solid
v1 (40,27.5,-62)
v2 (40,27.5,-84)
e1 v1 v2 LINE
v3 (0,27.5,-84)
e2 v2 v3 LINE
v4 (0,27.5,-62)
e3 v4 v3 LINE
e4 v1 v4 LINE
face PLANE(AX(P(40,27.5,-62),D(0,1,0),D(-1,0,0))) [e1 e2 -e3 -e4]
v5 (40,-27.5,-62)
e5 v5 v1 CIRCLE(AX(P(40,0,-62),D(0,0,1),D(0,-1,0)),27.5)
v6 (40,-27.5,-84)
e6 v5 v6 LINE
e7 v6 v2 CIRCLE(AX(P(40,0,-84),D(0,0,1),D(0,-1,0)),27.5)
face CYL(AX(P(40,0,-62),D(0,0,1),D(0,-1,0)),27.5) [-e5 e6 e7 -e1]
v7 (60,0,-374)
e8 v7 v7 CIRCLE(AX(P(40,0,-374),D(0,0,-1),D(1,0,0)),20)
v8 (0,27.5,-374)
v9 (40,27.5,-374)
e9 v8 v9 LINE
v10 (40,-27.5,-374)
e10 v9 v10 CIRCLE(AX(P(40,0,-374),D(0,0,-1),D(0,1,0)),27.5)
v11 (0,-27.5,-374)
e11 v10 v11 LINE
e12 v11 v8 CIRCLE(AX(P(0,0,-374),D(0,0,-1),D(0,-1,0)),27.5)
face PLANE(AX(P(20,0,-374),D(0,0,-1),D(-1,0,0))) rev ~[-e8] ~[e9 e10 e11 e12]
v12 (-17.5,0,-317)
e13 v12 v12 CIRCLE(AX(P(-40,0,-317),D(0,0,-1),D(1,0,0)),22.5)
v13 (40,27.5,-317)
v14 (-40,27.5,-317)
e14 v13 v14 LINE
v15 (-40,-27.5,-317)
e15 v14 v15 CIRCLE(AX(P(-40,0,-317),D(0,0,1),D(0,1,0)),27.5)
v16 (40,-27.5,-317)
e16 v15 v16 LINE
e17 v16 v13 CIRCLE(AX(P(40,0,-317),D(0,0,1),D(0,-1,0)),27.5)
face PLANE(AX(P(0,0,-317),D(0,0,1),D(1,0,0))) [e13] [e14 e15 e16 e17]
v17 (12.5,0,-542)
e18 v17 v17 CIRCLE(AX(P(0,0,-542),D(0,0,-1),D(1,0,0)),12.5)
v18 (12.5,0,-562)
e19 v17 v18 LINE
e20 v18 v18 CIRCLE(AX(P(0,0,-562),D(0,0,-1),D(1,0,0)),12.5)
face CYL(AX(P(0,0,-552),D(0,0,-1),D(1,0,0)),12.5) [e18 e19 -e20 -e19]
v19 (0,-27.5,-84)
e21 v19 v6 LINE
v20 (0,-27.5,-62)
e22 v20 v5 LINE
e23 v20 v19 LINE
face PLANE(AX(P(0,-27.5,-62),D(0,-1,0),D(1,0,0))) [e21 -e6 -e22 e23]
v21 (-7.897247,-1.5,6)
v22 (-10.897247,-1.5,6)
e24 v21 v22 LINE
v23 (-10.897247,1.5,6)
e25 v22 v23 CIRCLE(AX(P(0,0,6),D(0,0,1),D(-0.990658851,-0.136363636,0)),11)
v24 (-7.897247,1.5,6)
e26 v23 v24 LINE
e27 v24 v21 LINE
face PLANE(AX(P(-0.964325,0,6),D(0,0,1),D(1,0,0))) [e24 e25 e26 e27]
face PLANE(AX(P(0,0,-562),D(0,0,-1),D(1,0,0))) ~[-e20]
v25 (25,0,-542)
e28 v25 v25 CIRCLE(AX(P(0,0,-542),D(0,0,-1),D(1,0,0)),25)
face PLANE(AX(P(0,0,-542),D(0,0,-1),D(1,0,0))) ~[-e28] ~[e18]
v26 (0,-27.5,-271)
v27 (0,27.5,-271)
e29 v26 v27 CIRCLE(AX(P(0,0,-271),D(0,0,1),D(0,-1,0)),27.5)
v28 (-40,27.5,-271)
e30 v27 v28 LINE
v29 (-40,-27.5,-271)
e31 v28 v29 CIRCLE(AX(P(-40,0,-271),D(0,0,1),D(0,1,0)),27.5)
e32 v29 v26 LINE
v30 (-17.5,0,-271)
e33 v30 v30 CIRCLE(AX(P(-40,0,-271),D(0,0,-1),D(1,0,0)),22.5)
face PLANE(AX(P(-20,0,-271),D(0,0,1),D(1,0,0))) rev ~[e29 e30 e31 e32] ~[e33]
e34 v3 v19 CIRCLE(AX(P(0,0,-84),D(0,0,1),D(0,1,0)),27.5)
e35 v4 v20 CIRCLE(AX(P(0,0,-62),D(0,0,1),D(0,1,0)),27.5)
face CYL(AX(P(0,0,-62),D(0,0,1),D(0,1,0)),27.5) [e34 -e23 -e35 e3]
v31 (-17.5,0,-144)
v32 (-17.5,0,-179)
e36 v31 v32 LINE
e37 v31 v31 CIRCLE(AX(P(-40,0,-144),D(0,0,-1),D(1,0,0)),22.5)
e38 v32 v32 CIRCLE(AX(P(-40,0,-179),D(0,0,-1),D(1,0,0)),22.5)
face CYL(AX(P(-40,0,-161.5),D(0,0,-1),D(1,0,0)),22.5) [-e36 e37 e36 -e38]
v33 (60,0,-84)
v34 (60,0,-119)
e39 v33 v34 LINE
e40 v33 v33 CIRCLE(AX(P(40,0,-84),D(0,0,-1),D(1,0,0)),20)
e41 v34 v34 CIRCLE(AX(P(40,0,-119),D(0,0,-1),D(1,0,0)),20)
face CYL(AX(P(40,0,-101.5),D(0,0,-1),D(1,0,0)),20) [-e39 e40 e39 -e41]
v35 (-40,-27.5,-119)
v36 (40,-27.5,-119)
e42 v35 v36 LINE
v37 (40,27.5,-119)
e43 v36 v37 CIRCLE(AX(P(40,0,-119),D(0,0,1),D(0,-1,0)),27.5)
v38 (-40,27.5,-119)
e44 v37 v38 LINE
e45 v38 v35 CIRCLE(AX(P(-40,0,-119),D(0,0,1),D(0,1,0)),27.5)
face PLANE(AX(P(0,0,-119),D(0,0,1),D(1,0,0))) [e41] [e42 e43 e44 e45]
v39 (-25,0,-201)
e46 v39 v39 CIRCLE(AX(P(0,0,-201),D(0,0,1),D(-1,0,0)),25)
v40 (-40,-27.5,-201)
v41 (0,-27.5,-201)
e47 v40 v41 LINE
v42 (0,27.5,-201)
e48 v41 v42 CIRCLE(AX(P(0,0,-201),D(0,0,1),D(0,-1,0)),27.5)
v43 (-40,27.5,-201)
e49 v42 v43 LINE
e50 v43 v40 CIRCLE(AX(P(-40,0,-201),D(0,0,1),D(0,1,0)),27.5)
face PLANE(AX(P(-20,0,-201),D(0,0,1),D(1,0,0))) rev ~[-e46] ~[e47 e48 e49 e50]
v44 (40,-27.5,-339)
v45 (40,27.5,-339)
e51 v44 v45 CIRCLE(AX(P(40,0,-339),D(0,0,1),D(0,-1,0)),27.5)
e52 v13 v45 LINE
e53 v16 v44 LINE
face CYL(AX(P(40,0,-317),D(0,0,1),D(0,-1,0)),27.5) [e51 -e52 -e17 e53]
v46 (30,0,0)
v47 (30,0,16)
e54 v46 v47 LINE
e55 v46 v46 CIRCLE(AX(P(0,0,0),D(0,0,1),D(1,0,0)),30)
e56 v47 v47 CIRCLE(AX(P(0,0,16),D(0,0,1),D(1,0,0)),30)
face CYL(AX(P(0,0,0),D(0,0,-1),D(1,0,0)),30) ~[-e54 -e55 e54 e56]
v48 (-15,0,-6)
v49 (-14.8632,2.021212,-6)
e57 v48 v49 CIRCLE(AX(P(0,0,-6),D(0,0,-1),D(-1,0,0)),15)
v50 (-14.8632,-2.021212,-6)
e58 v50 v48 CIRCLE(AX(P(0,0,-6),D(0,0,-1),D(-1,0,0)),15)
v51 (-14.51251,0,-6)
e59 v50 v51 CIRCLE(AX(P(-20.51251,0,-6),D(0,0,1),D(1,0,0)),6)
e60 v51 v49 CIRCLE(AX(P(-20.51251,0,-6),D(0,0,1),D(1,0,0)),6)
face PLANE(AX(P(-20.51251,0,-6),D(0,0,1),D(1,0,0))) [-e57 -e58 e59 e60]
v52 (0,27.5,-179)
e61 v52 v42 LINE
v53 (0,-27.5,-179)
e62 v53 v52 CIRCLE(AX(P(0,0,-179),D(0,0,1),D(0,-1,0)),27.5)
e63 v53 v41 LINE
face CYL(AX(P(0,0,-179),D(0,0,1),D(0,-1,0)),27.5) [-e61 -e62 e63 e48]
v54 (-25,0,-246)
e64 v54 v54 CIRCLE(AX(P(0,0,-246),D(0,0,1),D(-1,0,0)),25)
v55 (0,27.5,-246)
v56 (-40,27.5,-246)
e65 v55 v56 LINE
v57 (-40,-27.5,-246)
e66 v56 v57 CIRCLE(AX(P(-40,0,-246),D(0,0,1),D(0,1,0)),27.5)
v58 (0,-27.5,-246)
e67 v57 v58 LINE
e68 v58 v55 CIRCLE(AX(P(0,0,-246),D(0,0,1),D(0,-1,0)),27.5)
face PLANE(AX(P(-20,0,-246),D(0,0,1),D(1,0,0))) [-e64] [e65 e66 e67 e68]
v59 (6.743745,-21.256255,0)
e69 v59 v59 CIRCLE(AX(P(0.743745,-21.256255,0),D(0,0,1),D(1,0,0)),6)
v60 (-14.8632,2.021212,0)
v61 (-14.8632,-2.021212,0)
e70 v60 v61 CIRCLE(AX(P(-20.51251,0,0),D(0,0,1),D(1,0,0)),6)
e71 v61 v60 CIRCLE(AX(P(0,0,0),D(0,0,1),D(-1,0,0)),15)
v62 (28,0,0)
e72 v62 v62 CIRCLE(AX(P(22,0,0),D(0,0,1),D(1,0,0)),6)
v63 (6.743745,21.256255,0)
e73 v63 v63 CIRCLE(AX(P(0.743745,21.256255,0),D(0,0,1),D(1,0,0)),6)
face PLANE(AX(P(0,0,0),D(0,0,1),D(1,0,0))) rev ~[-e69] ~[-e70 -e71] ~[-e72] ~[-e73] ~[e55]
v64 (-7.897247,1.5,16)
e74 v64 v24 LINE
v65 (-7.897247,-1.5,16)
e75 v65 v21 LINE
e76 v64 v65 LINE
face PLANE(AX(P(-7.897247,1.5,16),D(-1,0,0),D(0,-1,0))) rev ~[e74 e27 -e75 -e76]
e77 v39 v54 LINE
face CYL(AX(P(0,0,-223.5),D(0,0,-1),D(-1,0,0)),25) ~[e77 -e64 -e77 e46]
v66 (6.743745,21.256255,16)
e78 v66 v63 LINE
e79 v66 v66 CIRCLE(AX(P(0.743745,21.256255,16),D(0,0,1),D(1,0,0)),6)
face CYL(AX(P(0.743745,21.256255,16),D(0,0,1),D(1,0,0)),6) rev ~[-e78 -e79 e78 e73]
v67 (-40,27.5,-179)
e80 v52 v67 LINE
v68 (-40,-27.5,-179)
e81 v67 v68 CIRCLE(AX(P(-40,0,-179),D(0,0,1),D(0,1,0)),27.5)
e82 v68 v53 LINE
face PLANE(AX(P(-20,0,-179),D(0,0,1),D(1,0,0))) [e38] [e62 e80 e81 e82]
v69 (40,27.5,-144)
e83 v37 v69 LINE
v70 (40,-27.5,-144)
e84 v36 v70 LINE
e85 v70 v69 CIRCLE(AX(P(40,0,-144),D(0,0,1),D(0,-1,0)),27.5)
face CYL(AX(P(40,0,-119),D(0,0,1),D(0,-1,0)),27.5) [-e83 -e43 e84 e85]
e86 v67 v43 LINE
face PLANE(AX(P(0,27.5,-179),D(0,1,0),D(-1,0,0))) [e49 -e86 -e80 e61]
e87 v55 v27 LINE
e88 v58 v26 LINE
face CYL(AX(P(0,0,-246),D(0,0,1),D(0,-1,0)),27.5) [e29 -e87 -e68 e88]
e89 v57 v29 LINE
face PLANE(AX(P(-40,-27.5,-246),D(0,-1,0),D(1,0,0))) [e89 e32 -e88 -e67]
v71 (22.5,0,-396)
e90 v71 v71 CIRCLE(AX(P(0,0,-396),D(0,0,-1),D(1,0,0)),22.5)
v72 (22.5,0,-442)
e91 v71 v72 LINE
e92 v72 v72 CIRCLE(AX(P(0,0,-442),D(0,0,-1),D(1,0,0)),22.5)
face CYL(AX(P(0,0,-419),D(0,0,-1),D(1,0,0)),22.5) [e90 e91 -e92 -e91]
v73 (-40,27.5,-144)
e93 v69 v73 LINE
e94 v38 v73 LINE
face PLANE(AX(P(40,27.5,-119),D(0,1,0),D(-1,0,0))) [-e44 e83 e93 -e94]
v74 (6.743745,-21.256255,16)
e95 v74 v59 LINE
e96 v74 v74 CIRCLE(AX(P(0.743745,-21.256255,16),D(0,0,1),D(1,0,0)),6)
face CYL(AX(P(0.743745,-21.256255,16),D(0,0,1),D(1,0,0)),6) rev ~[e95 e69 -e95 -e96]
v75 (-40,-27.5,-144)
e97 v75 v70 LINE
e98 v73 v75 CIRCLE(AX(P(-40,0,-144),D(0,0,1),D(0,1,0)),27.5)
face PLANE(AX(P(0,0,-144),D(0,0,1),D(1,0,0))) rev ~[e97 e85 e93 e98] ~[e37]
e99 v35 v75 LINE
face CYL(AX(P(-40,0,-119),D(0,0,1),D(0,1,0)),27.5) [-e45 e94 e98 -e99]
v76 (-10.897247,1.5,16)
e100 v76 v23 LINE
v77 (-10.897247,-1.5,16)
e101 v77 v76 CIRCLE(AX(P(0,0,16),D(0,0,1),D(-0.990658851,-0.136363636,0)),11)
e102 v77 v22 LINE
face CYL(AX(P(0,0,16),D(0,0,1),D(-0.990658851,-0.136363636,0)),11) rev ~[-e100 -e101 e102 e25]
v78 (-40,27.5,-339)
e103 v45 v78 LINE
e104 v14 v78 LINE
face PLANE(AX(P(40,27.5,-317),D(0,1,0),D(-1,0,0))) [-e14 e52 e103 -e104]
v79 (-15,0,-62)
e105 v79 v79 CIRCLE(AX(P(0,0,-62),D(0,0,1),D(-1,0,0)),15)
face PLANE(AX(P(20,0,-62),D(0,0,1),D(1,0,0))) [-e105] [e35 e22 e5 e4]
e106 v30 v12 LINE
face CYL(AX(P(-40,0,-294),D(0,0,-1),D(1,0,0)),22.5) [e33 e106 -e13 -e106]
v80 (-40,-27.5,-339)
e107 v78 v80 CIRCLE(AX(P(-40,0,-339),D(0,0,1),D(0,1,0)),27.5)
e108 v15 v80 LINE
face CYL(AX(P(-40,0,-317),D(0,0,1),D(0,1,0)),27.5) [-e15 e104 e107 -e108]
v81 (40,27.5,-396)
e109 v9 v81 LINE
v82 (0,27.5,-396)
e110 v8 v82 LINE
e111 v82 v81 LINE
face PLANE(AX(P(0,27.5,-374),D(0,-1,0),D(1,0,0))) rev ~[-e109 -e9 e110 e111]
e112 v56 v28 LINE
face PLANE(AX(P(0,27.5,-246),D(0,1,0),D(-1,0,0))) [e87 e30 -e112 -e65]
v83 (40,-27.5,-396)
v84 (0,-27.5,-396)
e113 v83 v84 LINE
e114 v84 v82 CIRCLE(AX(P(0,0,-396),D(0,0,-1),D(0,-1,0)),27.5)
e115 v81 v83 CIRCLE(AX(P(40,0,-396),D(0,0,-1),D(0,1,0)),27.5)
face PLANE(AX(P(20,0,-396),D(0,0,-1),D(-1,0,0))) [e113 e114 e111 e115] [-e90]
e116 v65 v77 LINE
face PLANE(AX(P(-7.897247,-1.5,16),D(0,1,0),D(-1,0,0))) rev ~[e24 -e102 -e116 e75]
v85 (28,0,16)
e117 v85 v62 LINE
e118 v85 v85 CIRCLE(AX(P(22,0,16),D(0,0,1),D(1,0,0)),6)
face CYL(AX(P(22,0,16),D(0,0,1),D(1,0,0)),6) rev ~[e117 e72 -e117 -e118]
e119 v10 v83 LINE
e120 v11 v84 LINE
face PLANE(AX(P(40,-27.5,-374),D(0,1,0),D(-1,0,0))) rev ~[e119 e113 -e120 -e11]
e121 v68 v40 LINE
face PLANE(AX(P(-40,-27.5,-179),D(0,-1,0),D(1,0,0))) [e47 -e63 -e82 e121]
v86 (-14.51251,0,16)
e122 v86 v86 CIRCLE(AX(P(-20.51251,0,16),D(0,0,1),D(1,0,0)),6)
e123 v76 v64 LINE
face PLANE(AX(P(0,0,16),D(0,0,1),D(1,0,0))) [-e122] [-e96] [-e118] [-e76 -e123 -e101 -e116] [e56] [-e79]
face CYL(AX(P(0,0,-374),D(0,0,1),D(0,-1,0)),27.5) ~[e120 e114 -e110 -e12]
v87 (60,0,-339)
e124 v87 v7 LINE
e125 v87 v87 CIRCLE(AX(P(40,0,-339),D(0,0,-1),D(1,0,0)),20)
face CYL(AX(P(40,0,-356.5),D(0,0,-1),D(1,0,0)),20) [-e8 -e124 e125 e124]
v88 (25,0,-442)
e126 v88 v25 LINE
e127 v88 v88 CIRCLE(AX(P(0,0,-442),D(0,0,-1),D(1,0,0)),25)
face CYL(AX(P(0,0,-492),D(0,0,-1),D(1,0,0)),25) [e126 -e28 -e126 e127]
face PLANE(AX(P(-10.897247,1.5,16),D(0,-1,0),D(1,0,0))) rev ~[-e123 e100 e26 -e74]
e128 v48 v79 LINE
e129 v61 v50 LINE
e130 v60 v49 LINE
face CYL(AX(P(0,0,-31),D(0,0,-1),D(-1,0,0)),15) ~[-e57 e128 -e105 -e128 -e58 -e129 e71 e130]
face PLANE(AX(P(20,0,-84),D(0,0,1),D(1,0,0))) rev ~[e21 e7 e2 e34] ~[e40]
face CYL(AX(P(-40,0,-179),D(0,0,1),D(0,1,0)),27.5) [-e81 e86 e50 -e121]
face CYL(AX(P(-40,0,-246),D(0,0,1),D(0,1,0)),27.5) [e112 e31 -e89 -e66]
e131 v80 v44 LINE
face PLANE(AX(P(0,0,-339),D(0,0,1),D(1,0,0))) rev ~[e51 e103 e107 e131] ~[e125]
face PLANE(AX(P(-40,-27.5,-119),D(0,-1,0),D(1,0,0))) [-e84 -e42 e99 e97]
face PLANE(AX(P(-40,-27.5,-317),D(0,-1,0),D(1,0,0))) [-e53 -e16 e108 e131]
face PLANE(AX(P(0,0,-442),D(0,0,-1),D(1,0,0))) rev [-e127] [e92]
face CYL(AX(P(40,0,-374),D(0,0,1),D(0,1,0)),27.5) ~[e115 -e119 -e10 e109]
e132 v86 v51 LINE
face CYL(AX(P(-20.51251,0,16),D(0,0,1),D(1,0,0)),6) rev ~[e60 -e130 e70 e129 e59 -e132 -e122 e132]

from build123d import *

# Parameters (mm, degrees)
FLANGE_SKETCH_R              = 30
FRONT_FLANGE_60_DEPTH        = 16
FRONT_MAIN_JOURNAL_PROFILE_W = 15
FRONT_MAIN_JOURNAL_PROFILE_H = 62
CRANK_WEB_1_DEPTH            = 22
CRANKPIN_1_PROFILE_W         = 20
CRANKPIN_1_PROFILE_H         = 35
CRANK_WEB_2_DEPTH            = 25
MAIN_JOURNAL_2_PROFILE_W     = 22.5
MAIN_JOURNAL_2_PROFILE_H     = 35
CRANK_WEB_3_DEPTH            = 22
CRANKPIN_2_PROFILE_W         = 25
CRANKPIN_2_PROFILE_H         = 45
CRANK_WEB_4_DEPTH            = 25
MAIN_JOURNAL_3_PROFILE_W     = 22.5
MAIN_JOURNAL_3_PROFILE_H     = 46
CRANK_WEB_5_DEPTH            = 22
CRANKPIN_3_PROFILE_W         = 20
CRANKPIN_3_PROFILE_H         = 35
CRANK_WEB_6_SKETCH_R         = 20
CRANK_WEB_6_DEPTH            = 22
REAR_MAIN_JOURNAL_PROFILE_W  = 22.5
REAR_MAIN_JOURNAL_PROFILE_H  = 46
OUTPUT_SHAFT_PROFILE_W       = 25
OUTPUT_SHAFT_PROFILE_H       = 100
END_SPIGOT_PROFILE_W         = 12.5
END_SPIGOT_PROFILE_H         = 20
FLANGE_BOLT_HOLES_SKETCH_R   = 6
FLANGE_BOLT_HOLES_4X_DEPTH   = 22
FLANGE_CENTRE_RECESS_DEPTH   = 10


with BuildPart() as part:
    # Flange Sketch → Front Flange _60 (new body)
    with BuildSketch(Plane.XY):
        Circle(FLANGE_SKETCH_R)
    extrude(amount=FRONT_FLANGE_60_DEPTH)

    # Front Main Journal Profile → Front Main Journal (revolve)
    with BuildSketch(Plane(origin=(0, 0, 0), x_dir=(1, 0, 0), z_dir=(0, 1, 0)), mode=Mode.PRIVATE) as front_main_journal_sk:
        with Locations((7.5, 31)):
            Rectangle(FRONT_MAIN_JOURNAL_PROFILE_W, FRONT_MAIN_JOURNAL_PROFILE_H)
    revolve(front_main_journal_sk.sketch.rotate(Axis((0, 0, -63.530762812), (0, 0, 1)), 180), axis=Axis((0, 0, -63.530762812), (0, 0, 1)))

    # Crank Web 1 Sketch → Crank Web 1 (add)
    with BuildSketch(Plane(origin=(0, 0, -62), x_dir=(-1, 0, 0), z_dir=(0, 0, -1))):
        with BuildLine():
            Line((-40, 27.5), (0, 27.5))
            ThreePointArc((0, 27.5), (27.5, 0), (0, -27.5))
            Line((0, -27.5), (-40, -27.5))
            ThreePointArc((-40, -27.5), (-67.5, 0), (-40, 27.5))
        make_face()
    extrude(amount=CRANK_WEB_1_DEPTH)

    # Crankpin 1 Profile → Crankpin 1 (revolve)
    with BuildSketch(Plane(origin=(0, 0, 0), x_dir=(1, 0, 0), z_dir=(0, 1, 0))):
        with Locations((50, 101.5)):
            Rectangle(CRANKPIN_1_PROFILE_W, CRANKPIN_1_PROFILE_H)
    revolve(axis=Axis((40, 0, -84), (0, 0, -1)))

    # Crank Web 2 Sketch → Crank Web 2 (add)
    with BuildSketch(Plane(origin=(0, 0, -119), x_dir=(-1, 0, 0), z_dir=(0, 0, -1))):
        with BuildLine():
            Line((-40, 27.5), (40, 27.5))
            ThreePointArc((40, 27.5), (67.5, 0), (40, -27.5))
            Line((40, -27.5), (-40, -27.5))
            ThreePointArc((-40, -27.5), (-67.5, 0), (-40, 27.5))
        make_face()
    extrude(amount=CRANK_WEB_2_DEPTH)

    # Main Journal 2 Profile → Main Journal 2 (revolve)
    with BuildSketch(Plane(origin=(0, 0, 0), x_dir=(1, 0, 0), z_dir=(0, 1, 0))):
        with Locations((-28.75, 161.5)):
            Rectangle(MAIN_JOURNAL_2_PROFILE_W, MAIN_JOURNAL_2_PROFILE_H)
    revolve(axis=Axis((-40, 0, -144), (0, 0, -1)))

    # Crank Web 3 Sketch → Crank Web 3 (add)
    with BuildSketch(Plane(origin=(0, 0, -179), x_dir=(-1, 0, 0), z_dir=(0, 0, -1))):
        with BuildLine():
            Line((0, 27.5), (40, 27.5))
            ThreePointArc((40, 27.5), (67.5, 0), (40, -27.5))
            Line((40, -27.5), (0, -27.5))
            ThreePointArc((0, -27.5), (-27.5, 0), (0, 27.5))
        make_face()
    extrude(amount=CRANK_WEB_3_DEPTH)

    # Crankpin 2 Profile → Crankpin 2 (revolve)
    with BuildSketch(Plane(origin=(0, 0, 0), x_dir=(1, 0, 0), z_dir=(0, 1, 0)), mode=Mode.PRIVATE) as crankpin_2_sk:
        with Locations((12.5, 223.5)):
            Rectangle(CRANKPIN_2_PROFILE_W, CRANKPIN_2_PROFILE_H)
    revolve(crankpin_2_sk.sketch.rotate(Axis((0, 0, -261.148585065), (0, 0, 1)), 180), axis=Axis((0, 0, -261.148585065), (0, 0, 1)))

    # Crank Web 4 Sketch → Crank Web 4 (add)
    with BuildSketch(Plane(origin=(0, 0, -246), x_dir=(-1, 0, 0), z_dir=(0, 0, -1))):
        with BuildLine():
            Line((0, 27.5), (40, 27.5))
            ThreePointArc((40, 27.5), (67.5, 0), (40, -27.5))
            Line((40, -27.5), (0, -27.5))
            ThreePointArc((0, -27.5), (-27.5, 0), (0, 27.5))
        make_face()
    extrude(amount=CRANK_WEB_4_DEPTH)

    # Main Journal 3 Profile → Main Journal 3 (revolve)
    with BuildSketch(Plane(origin=(0, 0, 0), x_dir=(1, 0, 0), z_dir=(0, 1, 0))):
        with Locations((-28.75, 294)):
            Rectangle(MAIN_JOURNAL_3_PROFILE_W, MAIN_JOURNAL_3_PROFILE_H)
    revolve(axis=Axis((-40, 0, -271), (0, 0, -1)))

    # Crank Web 5 Sketch → Crank Web 5 (add)
    with BuildSketch(Plane(origin=(0, 0, -317), x_dir=(-1, 0, 0), z_dir=(0, 0, -1))):
        with BuildLine():
            Line((-40, 27.5), (40, 27.5))
            ThreePointArc((40, 27.5), (67.5, 0), (40, -27.5))
            Line((40, -27.5), (-40, -27.5))
            ThreePointArc((-40, -27.5), (-67.5, 0), (-40, 27.5))
        make_face()
    extrude(amount=CRANK_WEB_5_DEPTH)

    # Crankpin 3 Profile → Crankpin 3 (revolve)
    with BuildSketch(Plane(origin=(0, 0, 0), x_dir=(1, 0, 0), z_dir=(0, 1, 0))):
        with Locations((50, 356.5)):
            Rectangle(CRANKPIN_3_PROFILE_W, CRANKPIN_3_PROFILE_H)
    revolve(axis=Axis((40, 0, -339), (0, 0, -1)))

    # Crank Web 6 Sketch → Crank Web 6 (add)
    # profile 1 of 2: a face of its own
    with BuildSketch(Plane(origin=(0, 0, -374), x_dir=(-1, 0, 0), z_dir=(0, 0, -1))):
        with BuildLine():
            Line((-40, -27.5), (0, -27.5))
            ThreePointArc((0, -27.5), (27.5, 0), (0, 27.5))
            Line((0, 27.5), (-40, 27.5))
            ThreePointArc((-40, 27.5), (-67.5, 0), (-40, -27.5))
        make_face()
        with Locations(Location((-40, 0, 0), (0, 0, 180))):
            Circle(CRANK_WEB_6_SKETCH_R, mode=Mode.SUBTRACT)
    # profile 2 of 2: a face of its own
    with BuildSketch(Plane(origin=(0, 0, -374), x_dir=(-1, 0, 0), z_dir=(0, 0, -1))):
        with Locations(Location((-40, 0, 0), (0, 0, 180))):
            Circle(CRANK_WEB_6_SKETCH_R)
    extrude(amount=CRANK_WEB_6_DEPTH)

    # Rear Main Journal Profile → Rear Main Journal (revolve)
    with BuildSketch(Plane(origin=(0, 0, 0), x_dir=(1, 0, 0), z_dir=(0, 1, 0))):
        with Locations((11.25, 419)):
            Rectangle(REAR_MAIN_JOURNAL_PROFILE_W, REAR_MAIN_JOURNAL_PROFILE_H)
    revolve(axis=Axis((0, 0, -396), (0, 0, -1)))

    # Output Shaft Profile → Output Shaft (revolve)
    with BuildSketch(Plane(origin=(0, 0, 0), x_dir=(1, 0, 0), z_dir=(0, 1, 0))):
        with Locations((12.5, 492)):
            Rectangle(OUTPUT_SHAFT_PROFILE_W, OUTPUT_SHAFT_PROFILE_H)
    revolve(axis=Axis((0, 0, -442), (0, 0, -1)))

    # End Spigot Profile → End Spigot (revolve)
    with BuildSketch(Plane(origin=(0, 0, 0), x_dir=(1, 0, 0), z_dir=(0, 1, 0))):
        with Locations((6.25, 552)):
            Rectangle(END_SPIGOT_PROFILE_W, END_SPIGOT_PROFILE_H)
    revolve(axis=Axis((0, 0, -542), (0, 0, -1)))

    # Flange Bolt Holes Sketch → Flange Bolt Holes 4x (cut)
    with BuildSketch(Plane.XY.offset(16)):
        with Locations((22, 0)):
            Circle(FLANGE_BOLT_HOLES_SKETCH_R)
        with Locations((0.74374517, -21.25625483)):
            Circle(FLANGE_BOLT_HOLES_SKETCH_R)
        with Locations((-20.512509661, 0)):
            Circle(FLANGE_BOLT_HOLES_SKETCH_R)
        with Locations((0.74374517, 21.25625483)):
            Circle(FLANGE_BOLT_HOLES_SKETCH_R)
    extrude(amount=-FLANGE_BOLT_HOLES_4X_DEPTH, mode=Mode.SUBTRACT)

    # Flange Centre Recess Sketch → Flange Centre Recess (cut)
    with BuildSketch(Plane.XY.offset(16)):
        with BuildLine():
            Line((-10.897247359, 1.5), (-7.897247359, 1.5))
            Line((-7.897247359, 1.5), (-7.897247359, -1.5))
            Line((-7.897247359, -1.5), (-10.897247359, -1.5))
            ThreePointArc((-10.897247359, -1.5), (11, 0), (-10.897247359, 1.5))
        make_face()
    extrude(amount=-FLANGE_CENTRE_RECESS_DEPTH, mode=Mode.SUBTRACT)


solid = part.part
